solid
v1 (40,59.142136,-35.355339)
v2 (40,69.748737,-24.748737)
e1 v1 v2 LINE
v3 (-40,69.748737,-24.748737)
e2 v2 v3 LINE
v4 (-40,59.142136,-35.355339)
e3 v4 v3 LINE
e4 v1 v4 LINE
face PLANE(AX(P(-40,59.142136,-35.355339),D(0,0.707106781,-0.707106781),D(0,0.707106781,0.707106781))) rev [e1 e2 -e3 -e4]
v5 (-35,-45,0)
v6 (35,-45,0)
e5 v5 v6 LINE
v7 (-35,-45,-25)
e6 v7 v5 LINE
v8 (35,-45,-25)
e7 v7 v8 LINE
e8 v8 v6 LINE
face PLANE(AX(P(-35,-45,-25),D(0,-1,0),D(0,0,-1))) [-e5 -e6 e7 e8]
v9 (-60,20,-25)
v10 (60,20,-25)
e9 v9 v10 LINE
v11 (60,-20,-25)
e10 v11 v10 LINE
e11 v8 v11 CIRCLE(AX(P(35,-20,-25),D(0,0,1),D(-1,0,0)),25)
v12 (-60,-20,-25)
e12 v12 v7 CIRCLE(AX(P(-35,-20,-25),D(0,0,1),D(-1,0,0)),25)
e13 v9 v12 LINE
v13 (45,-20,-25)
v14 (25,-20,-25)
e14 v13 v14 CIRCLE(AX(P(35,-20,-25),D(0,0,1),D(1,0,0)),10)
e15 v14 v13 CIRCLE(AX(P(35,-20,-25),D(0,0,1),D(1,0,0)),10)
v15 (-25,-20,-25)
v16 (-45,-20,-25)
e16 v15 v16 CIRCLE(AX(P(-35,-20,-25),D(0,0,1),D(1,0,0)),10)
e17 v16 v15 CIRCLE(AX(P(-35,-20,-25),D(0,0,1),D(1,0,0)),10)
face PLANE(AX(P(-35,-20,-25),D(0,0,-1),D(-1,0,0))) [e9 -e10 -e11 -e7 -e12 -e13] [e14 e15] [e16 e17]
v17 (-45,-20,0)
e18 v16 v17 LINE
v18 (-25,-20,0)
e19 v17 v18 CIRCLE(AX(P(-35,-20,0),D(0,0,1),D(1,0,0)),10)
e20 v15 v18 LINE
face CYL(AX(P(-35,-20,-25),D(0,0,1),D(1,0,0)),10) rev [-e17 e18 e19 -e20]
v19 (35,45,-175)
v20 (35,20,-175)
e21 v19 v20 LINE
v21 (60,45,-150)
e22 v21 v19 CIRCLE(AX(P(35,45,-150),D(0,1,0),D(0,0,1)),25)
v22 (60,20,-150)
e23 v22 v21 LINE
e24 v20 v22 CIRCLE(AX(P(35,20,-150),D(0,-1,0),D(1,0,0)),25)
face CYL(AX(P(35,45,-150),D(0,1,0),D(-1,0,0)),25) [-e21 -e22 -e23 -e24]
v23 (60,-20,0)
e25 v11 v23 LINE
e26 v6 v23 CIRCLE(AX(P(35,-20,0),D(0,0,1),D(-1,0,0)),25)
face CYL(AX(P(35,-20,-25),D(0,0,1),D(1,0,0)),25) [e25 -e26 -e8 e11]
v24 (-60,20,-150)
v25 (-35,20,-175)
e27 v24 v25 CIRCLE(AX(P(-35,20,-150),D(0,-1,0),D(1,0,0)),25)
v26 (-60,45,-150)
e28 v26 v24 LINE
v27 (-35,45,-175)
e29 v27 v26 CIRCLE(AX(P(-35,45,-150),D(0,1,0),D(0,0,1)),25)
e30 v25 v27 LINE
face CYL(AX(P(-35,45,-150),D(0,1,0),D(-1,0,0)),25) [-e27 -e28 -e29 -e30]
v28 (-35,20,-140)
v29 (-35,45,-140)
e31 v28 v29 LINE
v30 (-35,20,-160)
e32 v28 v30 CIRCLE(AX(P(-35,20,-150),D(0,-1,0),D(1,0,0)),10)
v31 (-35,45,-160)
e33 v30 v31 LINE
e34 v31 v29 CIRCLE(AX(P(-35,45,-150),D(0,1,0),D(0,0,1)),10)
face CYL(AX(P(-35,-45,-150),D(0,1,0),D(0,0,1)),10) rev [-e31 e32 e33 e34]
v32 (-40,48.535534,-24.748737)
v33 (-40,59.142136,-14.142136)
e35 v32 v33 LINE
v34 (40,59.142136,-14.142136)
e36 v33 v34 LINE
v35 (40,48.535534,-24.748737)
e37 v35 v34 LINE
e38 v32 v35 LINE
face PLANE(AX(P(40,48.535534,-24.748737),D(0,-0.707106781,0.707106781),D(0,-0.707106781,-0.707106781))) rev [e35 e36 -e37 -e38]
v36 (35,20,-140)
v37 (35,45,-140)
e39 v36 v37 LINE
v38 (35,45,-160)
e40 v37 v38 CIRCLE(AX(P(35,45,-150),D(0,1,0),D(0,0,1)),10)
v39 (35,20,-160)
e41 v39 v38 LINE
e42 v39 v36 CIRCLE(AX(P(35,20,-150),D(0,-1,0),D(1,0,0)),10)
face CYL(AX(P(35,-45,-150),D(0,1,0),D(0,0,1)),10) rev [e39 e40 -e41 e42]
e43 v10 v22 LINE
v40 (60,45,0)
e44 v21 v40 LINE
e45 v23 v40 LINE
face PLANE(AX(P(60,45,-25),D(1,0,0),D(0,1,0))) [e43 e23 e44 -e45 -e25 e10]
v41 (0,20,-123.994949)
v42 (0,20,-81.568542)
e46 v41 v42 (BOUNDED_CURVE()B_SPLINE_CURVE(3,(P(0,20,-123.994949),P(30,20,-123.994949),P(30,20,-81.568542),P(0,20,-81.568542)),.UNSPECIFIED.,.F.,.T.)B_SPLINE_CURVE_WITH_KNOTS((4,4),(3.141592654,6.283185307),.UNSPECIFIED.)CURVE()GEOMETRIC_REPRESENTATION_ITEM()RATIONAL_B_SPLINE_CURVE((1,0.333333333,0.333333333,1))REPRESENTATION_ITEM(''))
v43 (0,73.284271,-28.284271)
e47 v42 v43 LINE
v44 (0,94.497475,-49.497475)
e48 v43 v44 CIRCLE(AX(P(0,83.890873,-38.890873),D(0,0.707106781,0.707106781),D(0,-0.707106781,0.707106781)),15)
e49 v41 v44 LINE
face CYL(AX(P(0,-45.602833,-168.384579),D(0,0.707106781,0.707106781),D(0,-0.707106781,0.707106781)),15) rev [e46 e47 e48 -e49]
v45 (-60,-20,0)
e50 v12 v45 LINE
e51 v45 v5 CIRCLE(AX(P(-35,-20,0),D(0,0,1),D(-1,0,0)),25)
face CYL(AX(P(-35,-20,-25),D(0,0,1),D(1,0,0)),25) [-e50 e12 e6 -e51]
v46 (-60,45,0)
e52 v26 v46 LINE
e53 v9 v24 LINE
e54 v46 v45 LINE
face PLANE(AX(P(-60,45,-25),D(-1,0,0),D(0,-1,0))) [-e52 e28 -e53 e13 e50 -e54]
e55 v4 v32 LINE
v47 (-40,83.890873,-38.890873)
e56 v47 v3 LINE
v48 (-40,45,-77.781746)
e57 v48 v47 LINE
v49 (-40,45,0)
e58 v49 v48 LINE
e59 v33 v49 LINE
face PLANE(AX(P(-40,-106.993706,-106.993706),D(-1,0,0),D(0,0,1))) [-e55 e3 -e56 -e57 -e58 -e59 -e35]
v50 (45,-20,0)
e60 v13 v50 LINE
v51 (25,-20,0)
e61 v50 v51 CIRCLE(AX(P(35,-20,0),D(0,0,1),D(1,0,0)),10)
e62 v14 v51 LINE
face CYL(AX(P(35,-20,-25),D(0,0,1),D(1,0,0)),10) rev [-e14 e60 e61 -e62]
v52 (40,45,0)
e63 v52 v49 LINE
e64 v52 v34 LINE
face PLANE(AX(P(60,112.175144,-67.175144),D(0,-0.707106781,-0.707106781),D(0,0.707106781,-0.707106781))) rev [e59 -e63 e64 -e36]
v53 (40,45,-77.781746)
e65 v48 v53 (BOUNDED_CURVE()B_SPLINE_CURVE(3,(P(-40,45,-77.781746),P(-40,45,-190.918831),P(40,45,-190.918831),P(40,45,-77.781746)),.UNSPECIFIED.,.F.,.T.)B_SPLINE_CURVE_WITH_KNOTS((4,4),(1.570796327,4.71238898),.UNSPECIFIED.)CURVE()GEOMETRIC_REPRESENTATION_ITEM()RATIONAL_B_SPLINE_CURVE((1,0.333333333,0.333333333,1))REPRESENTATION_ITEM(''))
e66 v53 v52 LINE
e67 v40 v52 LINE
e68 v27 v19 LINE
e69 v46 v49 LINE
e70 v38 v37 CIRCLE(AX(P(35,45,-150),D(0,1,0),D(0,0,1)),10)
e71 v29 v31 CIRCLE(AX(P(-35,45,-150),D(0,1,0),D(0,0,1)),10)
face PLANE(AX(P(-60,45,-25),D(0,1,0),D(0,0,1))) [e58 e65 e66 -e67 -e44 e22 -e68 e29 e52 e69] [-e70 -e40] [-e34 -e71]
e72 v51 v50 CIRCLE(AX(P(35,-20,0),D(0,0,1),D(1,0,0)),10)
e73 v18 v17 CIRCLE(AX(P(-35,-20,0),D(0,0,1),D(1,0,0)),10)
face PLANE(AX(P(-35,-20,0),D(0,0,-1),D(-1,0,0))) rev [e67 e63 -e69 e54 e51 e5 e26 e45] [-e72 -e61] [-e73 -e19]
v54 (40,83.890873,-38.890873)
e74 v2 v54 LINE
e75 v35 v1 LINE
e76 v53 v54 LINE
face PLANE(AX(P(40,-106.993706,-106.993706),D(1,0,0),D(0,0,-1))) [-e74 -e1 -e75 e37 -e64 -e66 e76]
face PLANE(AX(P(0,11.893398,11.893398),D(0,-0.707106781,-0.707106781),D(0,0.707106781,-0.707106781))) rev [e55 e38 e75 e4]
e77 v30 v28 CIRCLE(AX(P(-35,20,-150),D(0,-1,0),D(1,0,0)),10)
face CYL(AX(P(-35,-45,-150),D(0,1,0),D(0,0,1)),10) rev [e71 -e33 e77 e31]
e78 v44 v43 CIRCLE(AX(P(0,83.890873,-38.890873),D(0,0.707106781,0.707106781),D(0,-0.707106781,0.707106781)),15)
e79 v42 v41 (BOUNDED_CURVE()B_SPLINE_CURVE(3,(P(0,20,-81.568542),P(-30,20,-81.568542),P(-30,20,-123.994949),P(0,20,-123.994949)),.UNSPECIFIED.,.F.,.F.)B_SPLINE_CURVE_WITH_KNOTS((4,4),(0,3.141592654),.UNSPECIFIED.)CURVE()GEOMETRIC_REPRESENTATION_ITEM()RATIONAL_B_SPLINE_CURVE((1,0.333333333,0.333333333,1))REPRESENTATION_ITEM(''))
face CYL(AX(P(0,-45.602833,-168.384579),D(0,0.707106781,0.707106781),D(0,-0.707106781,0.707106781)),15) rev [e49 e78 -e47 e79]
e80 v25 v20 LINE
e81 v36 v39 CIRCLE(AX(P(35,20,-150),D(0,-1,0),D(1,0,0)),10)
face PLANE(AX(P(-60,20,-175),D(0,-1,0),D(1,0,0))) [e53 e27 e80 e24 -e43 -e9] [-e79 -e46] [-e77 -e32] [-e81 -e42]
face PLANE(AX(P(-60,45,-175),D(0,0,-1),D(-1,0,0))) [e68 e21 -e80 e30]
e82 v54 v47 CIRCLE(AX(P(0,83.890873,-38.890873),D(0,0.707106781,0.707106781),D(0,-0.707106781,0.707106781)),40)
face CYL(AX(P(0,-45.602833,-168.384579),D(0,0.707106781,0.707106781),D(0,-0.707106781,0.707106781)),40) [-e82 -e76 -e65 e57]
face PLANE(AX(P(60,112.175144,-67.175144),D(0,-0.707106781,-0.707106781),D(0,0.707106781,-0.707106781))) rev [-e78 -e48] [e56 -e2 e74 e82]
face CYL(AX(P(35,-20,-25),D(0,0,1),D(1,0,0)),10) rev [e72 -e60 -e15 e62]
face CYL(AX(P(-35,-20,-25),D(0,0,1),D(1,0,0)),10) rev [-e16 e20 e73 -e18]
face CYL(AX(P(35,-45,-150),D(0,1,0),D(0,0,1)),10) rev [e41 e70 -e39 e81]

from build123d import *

# Parameters (mm, degrees)
UPRIGHT_PLATE_SKETCH_R          = 10
UPRIGHT_PLATE_DEPTH             = 25
BASE_PLATE_SKETCH_W             = 150
BASE_PLATE_SKETCH_H             = 25
BASE_PLATE_DEPTH                = 120
BASE_PLATE_CORNER_FILLETS_R25_R = 25
BASE_PLATE_HOLES_SKETCH_R       = 10
BASE_PLATE_HOLES_DEPTH          = 206.730406114
WEDGE_SUPPORT_DEPTH             = 60
LUG_PROFILE_CUT_REACH           = 227.051
LUG_PROFILE_SKETCH_R            = 15
LUG_BORE_SKETCH_R               = 15
LUG_BORE_DEPTH                  = 226.05084201
LUG_SLOT_SKETCH_W               = 80
LUG_SLOT_SKETCH_H               = 15
LUG_SLOT_15X20_DEPTH            = 15


with BuildPart() as part:
    # Upright Plate Sketch → Upright Plate (new body)
    with BuildSketch(Plane.XY):
        with BuildLine():
            Line((-60, 45), (60, 45))
            Line((60, 45), (60, -20))
            ThreePointArc((60, -20), (52.67766953, -37.67766953), (35, -45))
            Line((35, -45), (-35, -45))
            ThreePointArc((-35, -45), (-52.67766953, -37.67766953), (-60, -20))
            Line((-60, -20), (-60, 45))
        make_face()
        with Locations((-35, -20)):
            Circle(UPRIGHT_PLATE_SKETCH_R, mode=Mode.SUBTRACT)
        with Locations((35, -20)):
            Circle(UPRIGHT_PLATE_SKETCH_R, mode=Mode.SUBTRACT)
    extrude(amount=-UPRIGHT_PLATE_DEPTH)

    # Base Plate Sketch → Base Plate (add)
    with BuildSketch(Plane(origin=(60, 0, 0), x_dir=(0, 0, -1), z_dir=(1, 0, 0))):
        with Locations((100, 32.5)):
            Rectangle(BASE_PLATE_SKETCH_W, BASE_PLATE_SKETCH_H)
    extrude(amount=-BASE_PLATE_DEPTH)

    # Base Plate Corner Fillets R25
    base_plate_corner_fillets_r25_edges = [part.edges().sort_by_distance(p)[0] for p in [
        (-60, 32.5, -175),
        (60, 32.5, -175),
    ]]
    fillet(base_plate_corner_fillets_r25_edges, radius=BASE_PLATE_CORNER_FILLETS_R25_R)

    # Base Plate Holes Sketch → Base Plate Holes (cut, through all)
    with BuildSketch(Plane(origin=(0, 45, 0), x_dir=(1, 0, 0), z_dir=(0, 1, 0))):
        with Locations(Location((35, 150, 0), (0, 0, 270))):
            Circle(BASE_PLATE_HOLES_SKETCH_R)
        with Locations(Location((-35, 150, 0), (0, 0, 270))):
            Circle(BASE_PLATE_HOLES_SKETCH_R)
    extrude(amount=-BASE_PLATE_HOLES_DEPTH, mode=Mode.SUBTRACT)

    # Wedge Support Sketch → Wedge Support (add, symmetric)
    with BuildSketch(Plane(origin=(0, 0, 0), x_dir=(0, 0, -1), z_dir=(1, 0, 0))):
        Polygon((134.350288425, 45), (67.175144213, 112.175144213), (0, 45), align=None)
    extrude(amount=WEDGE_SUPPORT_DEPTH, both=True)

    # Lug Profile Cut: up to this face of the body (flat: up to its plane)
    lug_profile_cut_end = Plane(part.part.faces().sort_by_distance((0, 45, -154.419772532))[0])
    # Lug Profile Sketch → Lug Profile Cut (cut, up to the picked face)
    with BuildSketch(Plane(origin=(0, 22.5, 22.5), x_dir=(1, 0, 0), z_dir=(0, 0.7071067811865485, 0.7071067811865467)), mode=Mode.PRIVATE) as lug_profile_cut_sk1:
        with BuildLine():
            Line((-40, 31.819805153), (-40, 86.819805153))
            ThreePointArc((-40, 86.819805153), (-28.284271247, 115.104076401), (0, 126.819805153))
            Line((0, 126.819805153), (-60, 126.819805153))
            Line((-60, 126.819805153), (-60, 31.819805153))
            Line((-60, 31.819805153), (-40, 31.819805153))
        make_face()
    lug_profile_cut_tool1 = split(extrude(lug_profile_cut_sk1.sketch, amount=-LUG_PROFILE_CUT_REACH, mode=Mode.PRIVATE), bisect_by=lug_profile_cut_end, keep=Keep.BOTH, mode=Mode.PRIVATE)
    # Lug Profile Sketch → Lug Profile Cut (cut, up to the picked face)
    with BuildSketch(Plane(origin=(0, 22.5, 22.5), x_dir=(1, 0, 0), z_dir=(0, 0.7071067811865485, 0.7071067811865467)), mode=Mode.PRIVATE) as lug_profile_cut_sk2:
        with BuildLine():
            Line((60, 126.819805153), (0, 126.819805153))
            ThreePointArc((0, 126.819805153), (28.284271247, 115.104076401), (40, 86.819805153))
            Line((40, 86.819805153), (40, 31.819805153))
            Line((40, 31.819805153), (60, 31.819805153))
            Line((60, 31.819805153), (60, 126.819805153))
        make_face()
    lug_profile_cut_tool2 = split(extrude(lug_profile_cut_sk2.sketch, amount=-LUG_PROFILE_CUT_REACH, mode=Mode.PRIVATE), bisect_by=lug_profile_cut_end, keep=Keep.BOTH, mode=Mode.PRIVATE)
    # Lug Profile Sketch → Lug Profile Cut (cut, up to the picked face)
    with BuildSketch(Plane(origin=(0, 22.5, 22.5), x_dir=(1, 0, 0), z_dir=(0, 0.7071067811865485, 0.7071067811865467)), mode=Mode.PRIVATE) as lug_profile_cut_sk3:
        with Locations(Location((0, 86.819805153, 0), (0, 0, 270))):
            Circle(LUG_PROFILE_SKETCH_R)
    lug_profile_cut_tool3 = split(extrude(lug_profile_cut_sk3.sketch, amount=-LUG_PROFILE_CUT_REACH, mode=Mode.PRIVATE), bisect_by=lug_profile_cut_end, keep=Keep.BOTH, mode=Mode.PRIVATE)
    add(lug_profile_cut_tool1.solids().sort_by(Axis((-47.101904, 82.761408, -37.761408), (0, -0.7071067811865485, -0.7071067811865467)))[0], mode=Mode.SUBTRACT)
    add(lug_profile_cut_tool2.solids().sort_by(Axis((47.101904, 82.761408, -37.761408), (0, -0.7071067811865485, -0.7071067811865467)))[0], mode=Mode.SUBTRACT)
    add(lug_profile_cut_tool3.solids().sort_by(Axis((0, 83.890873, -38.890873), (0, -0.7071067811865485, -0.7071067811865467)))[0], mode=Mode.SUBTRACT)

    # Lug Bore Sketch → Lug Bore (cut, through all)
    with BuildSketch(Plane(origin=(0, 22.5, 22.5), x_dir=(1, 0, 0), z_dir=(0, 0.7071067811865485, 0.7071067811865467))):
        with Locations(Location((0, 86.819805153, 0), (0, 0, 270))):
            Circle(LUG_BORE_SKETCH_R)
    extrude(amount=-LUG_BORE_DEPTH, mode=Mode.SUBTRACT)

    # Lug Slot Sketch → Lug Slot 15x20 (cut)
    with BuildSketch(Plane(origin=(0, 22.5, 22.5), x_dir=(1, 0, 0), z_dir=(0, 0.7071067811865485, 0.7071067811865467))):
        with Locations((0, 59.319805153)):
            Rectangle(LUG_SLOT_SKETCH_W, LUG_SLOT_SKETCH_H)
    extrude(amount=-LUG_SLOT_15X20_DEPTH, mode=Mode.SUBTRACT)


solid = part.part
